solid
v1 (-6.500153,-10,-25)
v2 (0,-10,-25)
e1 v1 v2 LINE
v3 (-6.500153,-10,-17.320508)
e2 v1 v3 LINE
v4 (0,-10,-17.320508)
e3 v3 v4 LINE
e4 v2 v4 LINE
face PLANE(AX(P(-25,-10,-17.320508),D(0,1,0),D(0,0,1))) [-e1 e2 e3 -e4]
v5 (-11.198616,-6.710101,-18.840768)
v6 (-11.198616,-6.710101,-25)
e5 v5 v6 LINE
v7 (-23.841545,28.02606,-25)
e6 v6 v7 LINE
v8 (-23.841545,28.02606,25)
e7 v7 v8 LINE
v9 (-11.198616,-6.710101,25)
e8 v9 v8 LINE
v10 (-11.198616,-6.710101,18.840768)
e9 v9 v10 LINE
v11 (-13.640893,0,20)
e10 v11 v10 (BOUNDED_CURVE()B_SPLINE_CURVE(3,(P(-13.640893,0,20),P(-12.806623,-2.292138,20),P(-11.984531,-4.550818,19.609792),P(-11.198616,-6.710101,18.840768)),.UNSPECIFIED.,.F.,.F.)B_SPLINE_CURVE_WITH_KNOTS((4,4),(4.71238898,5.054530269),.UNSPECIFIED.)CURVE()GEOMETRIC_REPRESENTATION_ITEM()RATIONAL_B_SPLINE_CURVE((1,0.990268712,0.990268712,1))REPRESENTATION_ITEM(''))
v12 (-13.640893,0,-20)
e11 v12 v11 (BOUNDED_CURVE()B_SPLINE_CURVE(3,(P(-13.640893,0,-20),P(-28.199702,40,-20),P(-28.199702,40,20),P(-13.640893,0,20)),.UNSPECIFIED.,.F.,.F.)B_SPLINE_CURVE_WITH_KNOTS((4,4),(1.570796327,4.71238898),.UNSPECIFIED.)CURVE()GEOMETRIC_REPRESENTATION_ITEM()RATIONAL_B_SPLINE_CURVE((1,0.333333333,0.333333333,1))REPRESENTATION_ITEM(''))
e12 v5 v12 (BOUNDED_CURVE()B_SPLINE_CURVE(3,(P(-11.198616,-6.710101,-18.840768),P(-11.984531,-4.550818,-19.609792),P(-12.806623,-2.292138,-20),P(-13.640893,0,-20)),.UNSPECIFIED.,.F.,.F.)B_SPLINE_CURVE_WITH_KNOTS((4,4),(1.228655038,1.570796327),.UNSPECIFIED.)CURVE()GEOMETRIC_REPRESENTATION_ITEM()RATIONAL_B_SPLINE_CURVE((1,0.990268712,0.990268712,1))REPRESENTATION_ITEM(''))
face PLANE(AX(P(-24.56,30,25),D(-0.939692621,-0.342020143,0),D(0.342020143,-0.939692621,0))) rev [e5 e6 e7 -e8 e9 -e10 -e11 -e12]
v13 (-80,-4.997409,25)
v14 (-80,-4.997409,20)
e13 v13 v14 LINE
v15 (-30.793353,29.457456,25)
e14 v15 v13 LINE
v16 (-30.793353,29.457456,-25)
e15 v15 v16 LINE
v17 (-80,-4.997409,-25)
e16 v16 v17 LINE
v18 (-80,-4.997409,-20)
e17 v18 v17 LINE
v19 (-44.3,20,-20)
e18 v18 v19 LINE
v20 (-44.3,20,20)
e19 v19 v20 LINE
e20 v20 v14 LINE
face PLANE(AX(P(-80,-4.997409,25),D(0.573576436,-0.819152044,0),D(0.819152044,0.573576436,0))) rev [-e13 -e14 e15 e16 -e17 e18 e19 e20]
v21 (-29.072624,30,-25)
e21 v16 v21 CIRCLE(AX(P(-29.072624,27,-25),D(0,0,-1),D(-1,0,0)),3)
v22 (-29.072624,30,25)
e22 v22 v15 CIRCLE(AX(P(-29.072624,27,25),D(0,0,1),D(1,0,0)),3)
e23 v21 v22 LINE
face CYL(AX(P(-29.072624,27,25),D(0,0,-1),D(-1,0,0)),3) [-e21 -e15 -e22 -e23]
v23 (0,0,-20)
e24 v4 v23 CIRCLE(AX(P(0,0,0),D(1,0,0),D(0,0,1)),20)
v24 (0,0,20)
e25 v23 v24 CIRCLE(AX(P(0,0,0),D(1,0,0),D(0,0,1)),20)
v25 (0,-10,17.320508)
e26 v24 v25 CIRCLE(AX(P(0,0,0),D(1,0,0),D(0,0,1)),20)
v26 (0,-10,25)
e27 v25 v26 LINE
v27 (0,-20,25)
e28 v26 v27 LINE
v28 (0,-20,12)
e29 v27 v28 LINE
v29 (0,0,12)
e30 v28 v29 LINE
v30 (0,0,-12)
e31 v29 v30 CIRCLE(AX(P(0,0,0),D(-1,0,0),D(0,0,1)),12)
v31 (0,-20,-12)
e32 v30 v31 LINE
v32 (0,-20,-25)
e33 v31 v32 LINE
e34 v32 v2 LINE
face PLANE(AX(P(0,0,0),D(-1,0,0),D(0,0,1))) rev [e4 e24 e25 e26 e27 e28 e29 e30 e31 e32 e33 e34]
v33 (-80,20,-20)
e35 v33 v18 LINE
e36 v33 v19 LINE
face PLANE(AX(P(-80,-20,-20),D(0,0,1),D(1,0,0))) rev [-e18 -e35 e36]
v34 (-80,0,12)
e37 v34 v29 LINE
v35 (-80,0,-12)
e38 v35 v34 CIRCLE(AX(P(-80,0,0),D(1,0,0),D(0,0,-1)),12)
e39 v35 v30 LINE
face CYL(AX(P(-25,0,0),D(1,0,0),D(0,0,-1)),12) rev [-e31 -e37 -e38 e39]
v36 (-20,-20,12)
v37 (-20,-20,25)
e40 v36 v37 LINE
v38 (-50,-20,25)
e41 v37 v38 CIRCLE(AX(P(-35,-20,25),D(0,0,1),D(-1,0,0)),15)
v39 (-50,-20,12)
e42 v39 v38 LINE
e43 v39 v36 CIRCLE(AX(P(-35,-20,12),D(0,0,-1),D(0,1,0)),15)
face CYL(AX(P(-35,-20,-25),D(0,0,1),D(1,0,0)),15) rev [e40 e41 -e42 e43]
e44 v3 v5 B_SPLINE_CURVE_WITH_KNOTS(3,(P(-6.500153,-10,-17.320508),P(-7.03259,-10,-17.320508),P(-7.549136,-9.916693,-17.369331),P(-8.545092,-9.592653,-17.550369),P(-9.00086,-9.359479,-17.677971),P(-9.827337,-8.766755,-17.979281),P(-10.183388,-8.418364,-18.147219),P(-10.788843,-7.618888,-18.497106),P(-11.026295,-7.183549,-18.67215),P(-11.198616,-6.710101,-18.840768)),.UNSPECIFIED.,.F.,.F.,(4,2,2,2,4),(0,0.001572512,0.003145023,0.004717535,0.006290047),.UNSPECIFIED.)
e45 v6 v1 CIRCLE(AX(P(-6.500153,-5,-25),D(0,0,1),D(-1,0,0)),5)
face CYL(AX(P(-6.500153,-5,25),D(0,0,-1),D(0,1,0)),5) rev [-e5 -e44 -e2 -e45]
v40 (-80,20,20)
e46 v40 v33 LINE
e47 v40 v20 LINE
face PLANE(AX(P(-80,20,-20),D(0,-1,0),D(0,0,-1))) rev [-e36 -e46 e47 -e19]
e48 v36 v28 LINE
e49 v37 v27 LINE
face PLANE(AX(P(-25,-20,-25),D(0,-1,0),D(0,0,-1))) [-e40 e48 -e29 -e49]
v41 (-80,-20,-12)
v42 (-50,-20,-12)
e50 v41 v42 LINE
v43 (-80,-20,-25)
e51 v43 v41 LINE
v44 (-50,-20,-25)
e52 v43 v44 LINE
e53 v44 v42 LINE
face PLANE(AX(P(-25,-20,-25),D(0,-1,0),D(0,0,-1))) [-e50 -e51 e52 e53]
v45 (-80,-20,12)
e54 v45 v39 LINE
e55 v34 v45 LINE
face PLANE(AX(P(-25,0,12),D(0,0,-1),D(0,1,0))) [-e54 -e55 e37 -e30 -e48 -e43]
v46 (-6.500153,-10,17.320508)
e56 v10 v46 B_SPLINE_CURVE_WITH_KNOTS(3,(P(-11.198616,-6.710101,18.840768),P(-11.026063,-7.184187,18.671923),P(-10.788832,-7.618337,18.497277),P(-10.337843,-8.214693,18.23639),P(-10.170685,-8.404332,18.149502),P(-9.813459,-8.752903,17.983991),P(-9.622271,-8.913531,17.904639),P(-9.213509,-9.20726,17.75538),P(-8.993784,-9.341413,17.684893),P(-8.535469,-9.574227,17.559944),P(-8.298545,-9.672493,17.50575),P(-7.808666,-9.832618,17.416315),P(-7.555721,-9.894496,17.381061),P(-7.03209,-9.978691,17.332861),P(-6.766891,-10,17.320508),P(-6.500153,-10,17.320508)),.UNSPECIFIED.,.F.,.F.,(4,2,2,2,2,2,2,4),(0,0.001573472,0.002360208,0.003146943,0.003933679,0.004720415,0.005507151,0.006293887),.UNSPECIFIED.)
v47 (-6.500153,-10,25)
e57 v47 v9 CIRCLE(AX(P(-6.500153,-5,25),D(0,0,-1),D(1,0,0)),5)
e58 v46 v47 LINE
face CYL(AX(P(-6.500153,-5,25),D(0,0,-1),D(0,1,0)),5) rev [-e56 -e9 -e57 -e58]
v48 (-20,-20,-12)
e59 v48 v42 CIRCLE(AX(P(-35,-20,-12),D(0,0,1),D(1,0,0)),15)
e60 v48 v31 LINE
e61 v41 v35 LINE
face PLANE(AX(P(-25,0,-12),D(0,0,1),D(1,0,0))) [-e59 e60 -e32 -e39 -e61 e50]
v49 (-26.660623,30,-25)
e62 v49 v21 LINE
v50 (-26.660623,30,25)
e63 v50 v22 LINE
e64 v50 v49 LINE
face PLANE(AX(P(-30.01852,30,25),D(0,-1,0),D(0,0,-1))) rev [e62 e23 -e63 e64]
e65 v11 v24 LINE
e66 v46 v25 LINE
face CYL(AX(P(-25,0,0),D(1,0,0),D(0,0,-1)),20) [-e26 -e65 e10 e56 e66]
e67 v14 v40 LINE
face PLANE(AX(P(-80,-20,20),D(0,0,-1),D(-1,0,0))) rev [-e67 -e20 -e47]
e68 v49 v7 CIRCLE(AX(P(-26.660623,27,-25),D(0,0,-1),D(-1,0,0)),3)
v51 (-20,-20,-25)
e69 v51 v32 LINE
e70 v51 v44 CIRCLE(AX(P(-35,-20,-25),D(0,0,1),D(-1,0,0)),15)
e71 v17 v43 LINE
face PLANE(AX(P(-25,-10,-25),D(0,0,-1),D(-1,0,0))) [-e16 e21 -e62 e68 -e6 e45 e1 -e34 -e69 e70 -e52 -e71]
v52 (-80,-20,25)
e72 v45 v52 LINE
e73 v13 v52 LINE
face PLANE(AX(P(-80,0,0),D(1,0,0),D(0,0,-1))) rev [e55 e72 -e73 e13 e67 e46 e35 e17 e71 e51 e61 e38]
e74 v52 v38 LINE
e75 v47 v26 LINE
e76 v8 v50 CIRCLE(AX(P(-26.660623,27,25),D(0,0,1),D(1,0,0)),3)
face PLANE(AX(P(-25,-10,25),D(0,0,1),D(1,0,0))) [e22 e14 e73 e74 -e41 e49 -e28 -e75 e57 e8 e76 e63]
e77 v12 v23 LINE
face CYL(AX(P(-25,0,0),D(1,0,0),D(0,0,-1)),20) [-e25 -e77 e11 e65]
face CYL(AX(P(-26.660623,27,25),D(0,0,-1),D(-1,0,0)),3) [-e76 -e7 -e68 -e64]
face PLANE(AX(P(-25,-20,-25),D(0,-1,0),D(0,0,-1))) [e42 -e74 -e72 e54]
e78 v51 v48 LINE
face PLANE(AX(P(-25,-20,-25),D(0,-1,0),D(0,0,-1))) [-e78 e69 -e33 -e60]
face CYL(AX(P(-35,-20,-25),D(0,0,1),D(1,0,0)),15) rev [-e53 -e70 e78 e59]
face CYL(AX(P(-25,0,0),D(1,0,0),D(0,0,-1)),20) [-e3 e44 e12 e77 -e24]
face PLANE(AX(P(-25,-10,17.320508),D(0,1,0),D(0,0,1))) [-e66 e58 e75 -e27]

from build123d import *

# Parameters (mm, degrees)
BASE_BLOCK_DEPTH         = 25
TOWER_SKETCH_40X40_W     = 40
TOWER_SKETCH_40X40_H     = 40
TOWER_BLOCK_DEPTH        = 55
RIDGE_SADDLE_BODY_DEPTH  = 25
RIDGE_FILLET_R3_R        = 3
SADDLE_OPENING_CUT_DEPTH = 90.022469074
RIDGE_GROOVE_CUT_DEPTH   = 99.994949366
EDGE_FILLET_R5_R         = 5


with BuildPart() as part:
    # Base Profile Sketch → Base Block (new body)
    with BuildSketch(Plane(origin=(0, 0, 0), x_dir=(0, 0, -1), z_dir=(1, 0, 0))):
        with BuildLine():
            Line((-17.320508076, -10), (-25, -10))
            Line((-25, -10), (-25, -20))
            Line((-25, -20), (-12, -20))
            Line((-12, -20), (-12, 0))
            ThreePointArc((-12, 0), (0, 12), (12, 0))
            Line((12, 0), (12, -20))
            Line((12, -20), (25, -20))
            Line((25, -20), (25, -10))
            Line((25, -10), (17.320508076, -10))
            ThreePointArc((17.320508076, -10), (0, 20), (-17.320508076, -10))
        make_face()
    extrude(amount=-BASE_BLOCK_DEPTH)

    # Tower Sketch 40x40 → Tower Block (add)
    with BuildSketch(Plane.ZY.offset(25)):
        Rectangle(TOWER_SKETCH_40X40_W, TOWER_SKETCH_40X40_H)
    extrude(amount=TOWER_BLOCK_DEPTH)

    # Ridge Profile Sketch → Ridge Saddle Body (add, symmetric)
    with BuildSketch(Plane.XY):
        Polygon((-80, -4.997409114), (-30.018519933, 30), (-24.56, 30), (-10.001190629, -10), (0, -10), (0, -20), (-80, -20), align=None)
    extrude(amount=RIDGE_SADDLE_BODY_DEPTH, both=True)

    # Ridge Fillet R3
    ridge_fillet_r3_edges = [part.edges().sort_by_distance(p)[0] for p in [
        (-30.018519933, 30, 0),
        (-24.56, 30, 0),
    ]]
    fillet(ridge_fillet_r3_edges, radius=RIDGE_FILLET_R3_R)

    # Saddle Opening Sketch → Saddle Opening Cut (cut, through all)
    with BuildSketch(Plane(origin=(0, 0, 0), x_dir=(0, 0, -1), z_dir=(1, 0, 0))):
        with BuildLine():
            Line((12, 0), (12, -10))
            Line((12, -10), (12, -20))
            Line((12, -20), (-12, -20))
            Line((-12, -20), (-12, -10))
            Line((-12, -10), (-12, 0))
            ThreePointArc((-12, 0), (0, 12), (12, 0))
        make_face()
    extrude(amount=-SADDLE_OPENING_CUT_DEPTH, mode=Mode.SUBTRACT)

    # Ridge Groove Sketch → Ridge Groove Cut (cut, through all)
    with BuildSketch(Plane.XY.offset(25)):
        with BuildLine():
            Line((-50, -20), (-20, -20))
            ThreePointArc((-20, -20), (-35, -5), (-50, -20))
        make_face()
    extrude(amount=-RIDGE_GROOVE_CUT_DEPTH, mode=Mode.SUBTRACT)

    # Edge Fillet R5
    edge_fillet_r5_edges = [part.edges().sort_by_distance(p)[0] for p in [
        (-10.001190629, -10, -21.160254038),
        (-10.001190629, -10, 21.160254038),
    ]]
    fillet(edge_fillet_r5_edges, radius=EDGE_FILLET_R5_R)


solid = part.part
